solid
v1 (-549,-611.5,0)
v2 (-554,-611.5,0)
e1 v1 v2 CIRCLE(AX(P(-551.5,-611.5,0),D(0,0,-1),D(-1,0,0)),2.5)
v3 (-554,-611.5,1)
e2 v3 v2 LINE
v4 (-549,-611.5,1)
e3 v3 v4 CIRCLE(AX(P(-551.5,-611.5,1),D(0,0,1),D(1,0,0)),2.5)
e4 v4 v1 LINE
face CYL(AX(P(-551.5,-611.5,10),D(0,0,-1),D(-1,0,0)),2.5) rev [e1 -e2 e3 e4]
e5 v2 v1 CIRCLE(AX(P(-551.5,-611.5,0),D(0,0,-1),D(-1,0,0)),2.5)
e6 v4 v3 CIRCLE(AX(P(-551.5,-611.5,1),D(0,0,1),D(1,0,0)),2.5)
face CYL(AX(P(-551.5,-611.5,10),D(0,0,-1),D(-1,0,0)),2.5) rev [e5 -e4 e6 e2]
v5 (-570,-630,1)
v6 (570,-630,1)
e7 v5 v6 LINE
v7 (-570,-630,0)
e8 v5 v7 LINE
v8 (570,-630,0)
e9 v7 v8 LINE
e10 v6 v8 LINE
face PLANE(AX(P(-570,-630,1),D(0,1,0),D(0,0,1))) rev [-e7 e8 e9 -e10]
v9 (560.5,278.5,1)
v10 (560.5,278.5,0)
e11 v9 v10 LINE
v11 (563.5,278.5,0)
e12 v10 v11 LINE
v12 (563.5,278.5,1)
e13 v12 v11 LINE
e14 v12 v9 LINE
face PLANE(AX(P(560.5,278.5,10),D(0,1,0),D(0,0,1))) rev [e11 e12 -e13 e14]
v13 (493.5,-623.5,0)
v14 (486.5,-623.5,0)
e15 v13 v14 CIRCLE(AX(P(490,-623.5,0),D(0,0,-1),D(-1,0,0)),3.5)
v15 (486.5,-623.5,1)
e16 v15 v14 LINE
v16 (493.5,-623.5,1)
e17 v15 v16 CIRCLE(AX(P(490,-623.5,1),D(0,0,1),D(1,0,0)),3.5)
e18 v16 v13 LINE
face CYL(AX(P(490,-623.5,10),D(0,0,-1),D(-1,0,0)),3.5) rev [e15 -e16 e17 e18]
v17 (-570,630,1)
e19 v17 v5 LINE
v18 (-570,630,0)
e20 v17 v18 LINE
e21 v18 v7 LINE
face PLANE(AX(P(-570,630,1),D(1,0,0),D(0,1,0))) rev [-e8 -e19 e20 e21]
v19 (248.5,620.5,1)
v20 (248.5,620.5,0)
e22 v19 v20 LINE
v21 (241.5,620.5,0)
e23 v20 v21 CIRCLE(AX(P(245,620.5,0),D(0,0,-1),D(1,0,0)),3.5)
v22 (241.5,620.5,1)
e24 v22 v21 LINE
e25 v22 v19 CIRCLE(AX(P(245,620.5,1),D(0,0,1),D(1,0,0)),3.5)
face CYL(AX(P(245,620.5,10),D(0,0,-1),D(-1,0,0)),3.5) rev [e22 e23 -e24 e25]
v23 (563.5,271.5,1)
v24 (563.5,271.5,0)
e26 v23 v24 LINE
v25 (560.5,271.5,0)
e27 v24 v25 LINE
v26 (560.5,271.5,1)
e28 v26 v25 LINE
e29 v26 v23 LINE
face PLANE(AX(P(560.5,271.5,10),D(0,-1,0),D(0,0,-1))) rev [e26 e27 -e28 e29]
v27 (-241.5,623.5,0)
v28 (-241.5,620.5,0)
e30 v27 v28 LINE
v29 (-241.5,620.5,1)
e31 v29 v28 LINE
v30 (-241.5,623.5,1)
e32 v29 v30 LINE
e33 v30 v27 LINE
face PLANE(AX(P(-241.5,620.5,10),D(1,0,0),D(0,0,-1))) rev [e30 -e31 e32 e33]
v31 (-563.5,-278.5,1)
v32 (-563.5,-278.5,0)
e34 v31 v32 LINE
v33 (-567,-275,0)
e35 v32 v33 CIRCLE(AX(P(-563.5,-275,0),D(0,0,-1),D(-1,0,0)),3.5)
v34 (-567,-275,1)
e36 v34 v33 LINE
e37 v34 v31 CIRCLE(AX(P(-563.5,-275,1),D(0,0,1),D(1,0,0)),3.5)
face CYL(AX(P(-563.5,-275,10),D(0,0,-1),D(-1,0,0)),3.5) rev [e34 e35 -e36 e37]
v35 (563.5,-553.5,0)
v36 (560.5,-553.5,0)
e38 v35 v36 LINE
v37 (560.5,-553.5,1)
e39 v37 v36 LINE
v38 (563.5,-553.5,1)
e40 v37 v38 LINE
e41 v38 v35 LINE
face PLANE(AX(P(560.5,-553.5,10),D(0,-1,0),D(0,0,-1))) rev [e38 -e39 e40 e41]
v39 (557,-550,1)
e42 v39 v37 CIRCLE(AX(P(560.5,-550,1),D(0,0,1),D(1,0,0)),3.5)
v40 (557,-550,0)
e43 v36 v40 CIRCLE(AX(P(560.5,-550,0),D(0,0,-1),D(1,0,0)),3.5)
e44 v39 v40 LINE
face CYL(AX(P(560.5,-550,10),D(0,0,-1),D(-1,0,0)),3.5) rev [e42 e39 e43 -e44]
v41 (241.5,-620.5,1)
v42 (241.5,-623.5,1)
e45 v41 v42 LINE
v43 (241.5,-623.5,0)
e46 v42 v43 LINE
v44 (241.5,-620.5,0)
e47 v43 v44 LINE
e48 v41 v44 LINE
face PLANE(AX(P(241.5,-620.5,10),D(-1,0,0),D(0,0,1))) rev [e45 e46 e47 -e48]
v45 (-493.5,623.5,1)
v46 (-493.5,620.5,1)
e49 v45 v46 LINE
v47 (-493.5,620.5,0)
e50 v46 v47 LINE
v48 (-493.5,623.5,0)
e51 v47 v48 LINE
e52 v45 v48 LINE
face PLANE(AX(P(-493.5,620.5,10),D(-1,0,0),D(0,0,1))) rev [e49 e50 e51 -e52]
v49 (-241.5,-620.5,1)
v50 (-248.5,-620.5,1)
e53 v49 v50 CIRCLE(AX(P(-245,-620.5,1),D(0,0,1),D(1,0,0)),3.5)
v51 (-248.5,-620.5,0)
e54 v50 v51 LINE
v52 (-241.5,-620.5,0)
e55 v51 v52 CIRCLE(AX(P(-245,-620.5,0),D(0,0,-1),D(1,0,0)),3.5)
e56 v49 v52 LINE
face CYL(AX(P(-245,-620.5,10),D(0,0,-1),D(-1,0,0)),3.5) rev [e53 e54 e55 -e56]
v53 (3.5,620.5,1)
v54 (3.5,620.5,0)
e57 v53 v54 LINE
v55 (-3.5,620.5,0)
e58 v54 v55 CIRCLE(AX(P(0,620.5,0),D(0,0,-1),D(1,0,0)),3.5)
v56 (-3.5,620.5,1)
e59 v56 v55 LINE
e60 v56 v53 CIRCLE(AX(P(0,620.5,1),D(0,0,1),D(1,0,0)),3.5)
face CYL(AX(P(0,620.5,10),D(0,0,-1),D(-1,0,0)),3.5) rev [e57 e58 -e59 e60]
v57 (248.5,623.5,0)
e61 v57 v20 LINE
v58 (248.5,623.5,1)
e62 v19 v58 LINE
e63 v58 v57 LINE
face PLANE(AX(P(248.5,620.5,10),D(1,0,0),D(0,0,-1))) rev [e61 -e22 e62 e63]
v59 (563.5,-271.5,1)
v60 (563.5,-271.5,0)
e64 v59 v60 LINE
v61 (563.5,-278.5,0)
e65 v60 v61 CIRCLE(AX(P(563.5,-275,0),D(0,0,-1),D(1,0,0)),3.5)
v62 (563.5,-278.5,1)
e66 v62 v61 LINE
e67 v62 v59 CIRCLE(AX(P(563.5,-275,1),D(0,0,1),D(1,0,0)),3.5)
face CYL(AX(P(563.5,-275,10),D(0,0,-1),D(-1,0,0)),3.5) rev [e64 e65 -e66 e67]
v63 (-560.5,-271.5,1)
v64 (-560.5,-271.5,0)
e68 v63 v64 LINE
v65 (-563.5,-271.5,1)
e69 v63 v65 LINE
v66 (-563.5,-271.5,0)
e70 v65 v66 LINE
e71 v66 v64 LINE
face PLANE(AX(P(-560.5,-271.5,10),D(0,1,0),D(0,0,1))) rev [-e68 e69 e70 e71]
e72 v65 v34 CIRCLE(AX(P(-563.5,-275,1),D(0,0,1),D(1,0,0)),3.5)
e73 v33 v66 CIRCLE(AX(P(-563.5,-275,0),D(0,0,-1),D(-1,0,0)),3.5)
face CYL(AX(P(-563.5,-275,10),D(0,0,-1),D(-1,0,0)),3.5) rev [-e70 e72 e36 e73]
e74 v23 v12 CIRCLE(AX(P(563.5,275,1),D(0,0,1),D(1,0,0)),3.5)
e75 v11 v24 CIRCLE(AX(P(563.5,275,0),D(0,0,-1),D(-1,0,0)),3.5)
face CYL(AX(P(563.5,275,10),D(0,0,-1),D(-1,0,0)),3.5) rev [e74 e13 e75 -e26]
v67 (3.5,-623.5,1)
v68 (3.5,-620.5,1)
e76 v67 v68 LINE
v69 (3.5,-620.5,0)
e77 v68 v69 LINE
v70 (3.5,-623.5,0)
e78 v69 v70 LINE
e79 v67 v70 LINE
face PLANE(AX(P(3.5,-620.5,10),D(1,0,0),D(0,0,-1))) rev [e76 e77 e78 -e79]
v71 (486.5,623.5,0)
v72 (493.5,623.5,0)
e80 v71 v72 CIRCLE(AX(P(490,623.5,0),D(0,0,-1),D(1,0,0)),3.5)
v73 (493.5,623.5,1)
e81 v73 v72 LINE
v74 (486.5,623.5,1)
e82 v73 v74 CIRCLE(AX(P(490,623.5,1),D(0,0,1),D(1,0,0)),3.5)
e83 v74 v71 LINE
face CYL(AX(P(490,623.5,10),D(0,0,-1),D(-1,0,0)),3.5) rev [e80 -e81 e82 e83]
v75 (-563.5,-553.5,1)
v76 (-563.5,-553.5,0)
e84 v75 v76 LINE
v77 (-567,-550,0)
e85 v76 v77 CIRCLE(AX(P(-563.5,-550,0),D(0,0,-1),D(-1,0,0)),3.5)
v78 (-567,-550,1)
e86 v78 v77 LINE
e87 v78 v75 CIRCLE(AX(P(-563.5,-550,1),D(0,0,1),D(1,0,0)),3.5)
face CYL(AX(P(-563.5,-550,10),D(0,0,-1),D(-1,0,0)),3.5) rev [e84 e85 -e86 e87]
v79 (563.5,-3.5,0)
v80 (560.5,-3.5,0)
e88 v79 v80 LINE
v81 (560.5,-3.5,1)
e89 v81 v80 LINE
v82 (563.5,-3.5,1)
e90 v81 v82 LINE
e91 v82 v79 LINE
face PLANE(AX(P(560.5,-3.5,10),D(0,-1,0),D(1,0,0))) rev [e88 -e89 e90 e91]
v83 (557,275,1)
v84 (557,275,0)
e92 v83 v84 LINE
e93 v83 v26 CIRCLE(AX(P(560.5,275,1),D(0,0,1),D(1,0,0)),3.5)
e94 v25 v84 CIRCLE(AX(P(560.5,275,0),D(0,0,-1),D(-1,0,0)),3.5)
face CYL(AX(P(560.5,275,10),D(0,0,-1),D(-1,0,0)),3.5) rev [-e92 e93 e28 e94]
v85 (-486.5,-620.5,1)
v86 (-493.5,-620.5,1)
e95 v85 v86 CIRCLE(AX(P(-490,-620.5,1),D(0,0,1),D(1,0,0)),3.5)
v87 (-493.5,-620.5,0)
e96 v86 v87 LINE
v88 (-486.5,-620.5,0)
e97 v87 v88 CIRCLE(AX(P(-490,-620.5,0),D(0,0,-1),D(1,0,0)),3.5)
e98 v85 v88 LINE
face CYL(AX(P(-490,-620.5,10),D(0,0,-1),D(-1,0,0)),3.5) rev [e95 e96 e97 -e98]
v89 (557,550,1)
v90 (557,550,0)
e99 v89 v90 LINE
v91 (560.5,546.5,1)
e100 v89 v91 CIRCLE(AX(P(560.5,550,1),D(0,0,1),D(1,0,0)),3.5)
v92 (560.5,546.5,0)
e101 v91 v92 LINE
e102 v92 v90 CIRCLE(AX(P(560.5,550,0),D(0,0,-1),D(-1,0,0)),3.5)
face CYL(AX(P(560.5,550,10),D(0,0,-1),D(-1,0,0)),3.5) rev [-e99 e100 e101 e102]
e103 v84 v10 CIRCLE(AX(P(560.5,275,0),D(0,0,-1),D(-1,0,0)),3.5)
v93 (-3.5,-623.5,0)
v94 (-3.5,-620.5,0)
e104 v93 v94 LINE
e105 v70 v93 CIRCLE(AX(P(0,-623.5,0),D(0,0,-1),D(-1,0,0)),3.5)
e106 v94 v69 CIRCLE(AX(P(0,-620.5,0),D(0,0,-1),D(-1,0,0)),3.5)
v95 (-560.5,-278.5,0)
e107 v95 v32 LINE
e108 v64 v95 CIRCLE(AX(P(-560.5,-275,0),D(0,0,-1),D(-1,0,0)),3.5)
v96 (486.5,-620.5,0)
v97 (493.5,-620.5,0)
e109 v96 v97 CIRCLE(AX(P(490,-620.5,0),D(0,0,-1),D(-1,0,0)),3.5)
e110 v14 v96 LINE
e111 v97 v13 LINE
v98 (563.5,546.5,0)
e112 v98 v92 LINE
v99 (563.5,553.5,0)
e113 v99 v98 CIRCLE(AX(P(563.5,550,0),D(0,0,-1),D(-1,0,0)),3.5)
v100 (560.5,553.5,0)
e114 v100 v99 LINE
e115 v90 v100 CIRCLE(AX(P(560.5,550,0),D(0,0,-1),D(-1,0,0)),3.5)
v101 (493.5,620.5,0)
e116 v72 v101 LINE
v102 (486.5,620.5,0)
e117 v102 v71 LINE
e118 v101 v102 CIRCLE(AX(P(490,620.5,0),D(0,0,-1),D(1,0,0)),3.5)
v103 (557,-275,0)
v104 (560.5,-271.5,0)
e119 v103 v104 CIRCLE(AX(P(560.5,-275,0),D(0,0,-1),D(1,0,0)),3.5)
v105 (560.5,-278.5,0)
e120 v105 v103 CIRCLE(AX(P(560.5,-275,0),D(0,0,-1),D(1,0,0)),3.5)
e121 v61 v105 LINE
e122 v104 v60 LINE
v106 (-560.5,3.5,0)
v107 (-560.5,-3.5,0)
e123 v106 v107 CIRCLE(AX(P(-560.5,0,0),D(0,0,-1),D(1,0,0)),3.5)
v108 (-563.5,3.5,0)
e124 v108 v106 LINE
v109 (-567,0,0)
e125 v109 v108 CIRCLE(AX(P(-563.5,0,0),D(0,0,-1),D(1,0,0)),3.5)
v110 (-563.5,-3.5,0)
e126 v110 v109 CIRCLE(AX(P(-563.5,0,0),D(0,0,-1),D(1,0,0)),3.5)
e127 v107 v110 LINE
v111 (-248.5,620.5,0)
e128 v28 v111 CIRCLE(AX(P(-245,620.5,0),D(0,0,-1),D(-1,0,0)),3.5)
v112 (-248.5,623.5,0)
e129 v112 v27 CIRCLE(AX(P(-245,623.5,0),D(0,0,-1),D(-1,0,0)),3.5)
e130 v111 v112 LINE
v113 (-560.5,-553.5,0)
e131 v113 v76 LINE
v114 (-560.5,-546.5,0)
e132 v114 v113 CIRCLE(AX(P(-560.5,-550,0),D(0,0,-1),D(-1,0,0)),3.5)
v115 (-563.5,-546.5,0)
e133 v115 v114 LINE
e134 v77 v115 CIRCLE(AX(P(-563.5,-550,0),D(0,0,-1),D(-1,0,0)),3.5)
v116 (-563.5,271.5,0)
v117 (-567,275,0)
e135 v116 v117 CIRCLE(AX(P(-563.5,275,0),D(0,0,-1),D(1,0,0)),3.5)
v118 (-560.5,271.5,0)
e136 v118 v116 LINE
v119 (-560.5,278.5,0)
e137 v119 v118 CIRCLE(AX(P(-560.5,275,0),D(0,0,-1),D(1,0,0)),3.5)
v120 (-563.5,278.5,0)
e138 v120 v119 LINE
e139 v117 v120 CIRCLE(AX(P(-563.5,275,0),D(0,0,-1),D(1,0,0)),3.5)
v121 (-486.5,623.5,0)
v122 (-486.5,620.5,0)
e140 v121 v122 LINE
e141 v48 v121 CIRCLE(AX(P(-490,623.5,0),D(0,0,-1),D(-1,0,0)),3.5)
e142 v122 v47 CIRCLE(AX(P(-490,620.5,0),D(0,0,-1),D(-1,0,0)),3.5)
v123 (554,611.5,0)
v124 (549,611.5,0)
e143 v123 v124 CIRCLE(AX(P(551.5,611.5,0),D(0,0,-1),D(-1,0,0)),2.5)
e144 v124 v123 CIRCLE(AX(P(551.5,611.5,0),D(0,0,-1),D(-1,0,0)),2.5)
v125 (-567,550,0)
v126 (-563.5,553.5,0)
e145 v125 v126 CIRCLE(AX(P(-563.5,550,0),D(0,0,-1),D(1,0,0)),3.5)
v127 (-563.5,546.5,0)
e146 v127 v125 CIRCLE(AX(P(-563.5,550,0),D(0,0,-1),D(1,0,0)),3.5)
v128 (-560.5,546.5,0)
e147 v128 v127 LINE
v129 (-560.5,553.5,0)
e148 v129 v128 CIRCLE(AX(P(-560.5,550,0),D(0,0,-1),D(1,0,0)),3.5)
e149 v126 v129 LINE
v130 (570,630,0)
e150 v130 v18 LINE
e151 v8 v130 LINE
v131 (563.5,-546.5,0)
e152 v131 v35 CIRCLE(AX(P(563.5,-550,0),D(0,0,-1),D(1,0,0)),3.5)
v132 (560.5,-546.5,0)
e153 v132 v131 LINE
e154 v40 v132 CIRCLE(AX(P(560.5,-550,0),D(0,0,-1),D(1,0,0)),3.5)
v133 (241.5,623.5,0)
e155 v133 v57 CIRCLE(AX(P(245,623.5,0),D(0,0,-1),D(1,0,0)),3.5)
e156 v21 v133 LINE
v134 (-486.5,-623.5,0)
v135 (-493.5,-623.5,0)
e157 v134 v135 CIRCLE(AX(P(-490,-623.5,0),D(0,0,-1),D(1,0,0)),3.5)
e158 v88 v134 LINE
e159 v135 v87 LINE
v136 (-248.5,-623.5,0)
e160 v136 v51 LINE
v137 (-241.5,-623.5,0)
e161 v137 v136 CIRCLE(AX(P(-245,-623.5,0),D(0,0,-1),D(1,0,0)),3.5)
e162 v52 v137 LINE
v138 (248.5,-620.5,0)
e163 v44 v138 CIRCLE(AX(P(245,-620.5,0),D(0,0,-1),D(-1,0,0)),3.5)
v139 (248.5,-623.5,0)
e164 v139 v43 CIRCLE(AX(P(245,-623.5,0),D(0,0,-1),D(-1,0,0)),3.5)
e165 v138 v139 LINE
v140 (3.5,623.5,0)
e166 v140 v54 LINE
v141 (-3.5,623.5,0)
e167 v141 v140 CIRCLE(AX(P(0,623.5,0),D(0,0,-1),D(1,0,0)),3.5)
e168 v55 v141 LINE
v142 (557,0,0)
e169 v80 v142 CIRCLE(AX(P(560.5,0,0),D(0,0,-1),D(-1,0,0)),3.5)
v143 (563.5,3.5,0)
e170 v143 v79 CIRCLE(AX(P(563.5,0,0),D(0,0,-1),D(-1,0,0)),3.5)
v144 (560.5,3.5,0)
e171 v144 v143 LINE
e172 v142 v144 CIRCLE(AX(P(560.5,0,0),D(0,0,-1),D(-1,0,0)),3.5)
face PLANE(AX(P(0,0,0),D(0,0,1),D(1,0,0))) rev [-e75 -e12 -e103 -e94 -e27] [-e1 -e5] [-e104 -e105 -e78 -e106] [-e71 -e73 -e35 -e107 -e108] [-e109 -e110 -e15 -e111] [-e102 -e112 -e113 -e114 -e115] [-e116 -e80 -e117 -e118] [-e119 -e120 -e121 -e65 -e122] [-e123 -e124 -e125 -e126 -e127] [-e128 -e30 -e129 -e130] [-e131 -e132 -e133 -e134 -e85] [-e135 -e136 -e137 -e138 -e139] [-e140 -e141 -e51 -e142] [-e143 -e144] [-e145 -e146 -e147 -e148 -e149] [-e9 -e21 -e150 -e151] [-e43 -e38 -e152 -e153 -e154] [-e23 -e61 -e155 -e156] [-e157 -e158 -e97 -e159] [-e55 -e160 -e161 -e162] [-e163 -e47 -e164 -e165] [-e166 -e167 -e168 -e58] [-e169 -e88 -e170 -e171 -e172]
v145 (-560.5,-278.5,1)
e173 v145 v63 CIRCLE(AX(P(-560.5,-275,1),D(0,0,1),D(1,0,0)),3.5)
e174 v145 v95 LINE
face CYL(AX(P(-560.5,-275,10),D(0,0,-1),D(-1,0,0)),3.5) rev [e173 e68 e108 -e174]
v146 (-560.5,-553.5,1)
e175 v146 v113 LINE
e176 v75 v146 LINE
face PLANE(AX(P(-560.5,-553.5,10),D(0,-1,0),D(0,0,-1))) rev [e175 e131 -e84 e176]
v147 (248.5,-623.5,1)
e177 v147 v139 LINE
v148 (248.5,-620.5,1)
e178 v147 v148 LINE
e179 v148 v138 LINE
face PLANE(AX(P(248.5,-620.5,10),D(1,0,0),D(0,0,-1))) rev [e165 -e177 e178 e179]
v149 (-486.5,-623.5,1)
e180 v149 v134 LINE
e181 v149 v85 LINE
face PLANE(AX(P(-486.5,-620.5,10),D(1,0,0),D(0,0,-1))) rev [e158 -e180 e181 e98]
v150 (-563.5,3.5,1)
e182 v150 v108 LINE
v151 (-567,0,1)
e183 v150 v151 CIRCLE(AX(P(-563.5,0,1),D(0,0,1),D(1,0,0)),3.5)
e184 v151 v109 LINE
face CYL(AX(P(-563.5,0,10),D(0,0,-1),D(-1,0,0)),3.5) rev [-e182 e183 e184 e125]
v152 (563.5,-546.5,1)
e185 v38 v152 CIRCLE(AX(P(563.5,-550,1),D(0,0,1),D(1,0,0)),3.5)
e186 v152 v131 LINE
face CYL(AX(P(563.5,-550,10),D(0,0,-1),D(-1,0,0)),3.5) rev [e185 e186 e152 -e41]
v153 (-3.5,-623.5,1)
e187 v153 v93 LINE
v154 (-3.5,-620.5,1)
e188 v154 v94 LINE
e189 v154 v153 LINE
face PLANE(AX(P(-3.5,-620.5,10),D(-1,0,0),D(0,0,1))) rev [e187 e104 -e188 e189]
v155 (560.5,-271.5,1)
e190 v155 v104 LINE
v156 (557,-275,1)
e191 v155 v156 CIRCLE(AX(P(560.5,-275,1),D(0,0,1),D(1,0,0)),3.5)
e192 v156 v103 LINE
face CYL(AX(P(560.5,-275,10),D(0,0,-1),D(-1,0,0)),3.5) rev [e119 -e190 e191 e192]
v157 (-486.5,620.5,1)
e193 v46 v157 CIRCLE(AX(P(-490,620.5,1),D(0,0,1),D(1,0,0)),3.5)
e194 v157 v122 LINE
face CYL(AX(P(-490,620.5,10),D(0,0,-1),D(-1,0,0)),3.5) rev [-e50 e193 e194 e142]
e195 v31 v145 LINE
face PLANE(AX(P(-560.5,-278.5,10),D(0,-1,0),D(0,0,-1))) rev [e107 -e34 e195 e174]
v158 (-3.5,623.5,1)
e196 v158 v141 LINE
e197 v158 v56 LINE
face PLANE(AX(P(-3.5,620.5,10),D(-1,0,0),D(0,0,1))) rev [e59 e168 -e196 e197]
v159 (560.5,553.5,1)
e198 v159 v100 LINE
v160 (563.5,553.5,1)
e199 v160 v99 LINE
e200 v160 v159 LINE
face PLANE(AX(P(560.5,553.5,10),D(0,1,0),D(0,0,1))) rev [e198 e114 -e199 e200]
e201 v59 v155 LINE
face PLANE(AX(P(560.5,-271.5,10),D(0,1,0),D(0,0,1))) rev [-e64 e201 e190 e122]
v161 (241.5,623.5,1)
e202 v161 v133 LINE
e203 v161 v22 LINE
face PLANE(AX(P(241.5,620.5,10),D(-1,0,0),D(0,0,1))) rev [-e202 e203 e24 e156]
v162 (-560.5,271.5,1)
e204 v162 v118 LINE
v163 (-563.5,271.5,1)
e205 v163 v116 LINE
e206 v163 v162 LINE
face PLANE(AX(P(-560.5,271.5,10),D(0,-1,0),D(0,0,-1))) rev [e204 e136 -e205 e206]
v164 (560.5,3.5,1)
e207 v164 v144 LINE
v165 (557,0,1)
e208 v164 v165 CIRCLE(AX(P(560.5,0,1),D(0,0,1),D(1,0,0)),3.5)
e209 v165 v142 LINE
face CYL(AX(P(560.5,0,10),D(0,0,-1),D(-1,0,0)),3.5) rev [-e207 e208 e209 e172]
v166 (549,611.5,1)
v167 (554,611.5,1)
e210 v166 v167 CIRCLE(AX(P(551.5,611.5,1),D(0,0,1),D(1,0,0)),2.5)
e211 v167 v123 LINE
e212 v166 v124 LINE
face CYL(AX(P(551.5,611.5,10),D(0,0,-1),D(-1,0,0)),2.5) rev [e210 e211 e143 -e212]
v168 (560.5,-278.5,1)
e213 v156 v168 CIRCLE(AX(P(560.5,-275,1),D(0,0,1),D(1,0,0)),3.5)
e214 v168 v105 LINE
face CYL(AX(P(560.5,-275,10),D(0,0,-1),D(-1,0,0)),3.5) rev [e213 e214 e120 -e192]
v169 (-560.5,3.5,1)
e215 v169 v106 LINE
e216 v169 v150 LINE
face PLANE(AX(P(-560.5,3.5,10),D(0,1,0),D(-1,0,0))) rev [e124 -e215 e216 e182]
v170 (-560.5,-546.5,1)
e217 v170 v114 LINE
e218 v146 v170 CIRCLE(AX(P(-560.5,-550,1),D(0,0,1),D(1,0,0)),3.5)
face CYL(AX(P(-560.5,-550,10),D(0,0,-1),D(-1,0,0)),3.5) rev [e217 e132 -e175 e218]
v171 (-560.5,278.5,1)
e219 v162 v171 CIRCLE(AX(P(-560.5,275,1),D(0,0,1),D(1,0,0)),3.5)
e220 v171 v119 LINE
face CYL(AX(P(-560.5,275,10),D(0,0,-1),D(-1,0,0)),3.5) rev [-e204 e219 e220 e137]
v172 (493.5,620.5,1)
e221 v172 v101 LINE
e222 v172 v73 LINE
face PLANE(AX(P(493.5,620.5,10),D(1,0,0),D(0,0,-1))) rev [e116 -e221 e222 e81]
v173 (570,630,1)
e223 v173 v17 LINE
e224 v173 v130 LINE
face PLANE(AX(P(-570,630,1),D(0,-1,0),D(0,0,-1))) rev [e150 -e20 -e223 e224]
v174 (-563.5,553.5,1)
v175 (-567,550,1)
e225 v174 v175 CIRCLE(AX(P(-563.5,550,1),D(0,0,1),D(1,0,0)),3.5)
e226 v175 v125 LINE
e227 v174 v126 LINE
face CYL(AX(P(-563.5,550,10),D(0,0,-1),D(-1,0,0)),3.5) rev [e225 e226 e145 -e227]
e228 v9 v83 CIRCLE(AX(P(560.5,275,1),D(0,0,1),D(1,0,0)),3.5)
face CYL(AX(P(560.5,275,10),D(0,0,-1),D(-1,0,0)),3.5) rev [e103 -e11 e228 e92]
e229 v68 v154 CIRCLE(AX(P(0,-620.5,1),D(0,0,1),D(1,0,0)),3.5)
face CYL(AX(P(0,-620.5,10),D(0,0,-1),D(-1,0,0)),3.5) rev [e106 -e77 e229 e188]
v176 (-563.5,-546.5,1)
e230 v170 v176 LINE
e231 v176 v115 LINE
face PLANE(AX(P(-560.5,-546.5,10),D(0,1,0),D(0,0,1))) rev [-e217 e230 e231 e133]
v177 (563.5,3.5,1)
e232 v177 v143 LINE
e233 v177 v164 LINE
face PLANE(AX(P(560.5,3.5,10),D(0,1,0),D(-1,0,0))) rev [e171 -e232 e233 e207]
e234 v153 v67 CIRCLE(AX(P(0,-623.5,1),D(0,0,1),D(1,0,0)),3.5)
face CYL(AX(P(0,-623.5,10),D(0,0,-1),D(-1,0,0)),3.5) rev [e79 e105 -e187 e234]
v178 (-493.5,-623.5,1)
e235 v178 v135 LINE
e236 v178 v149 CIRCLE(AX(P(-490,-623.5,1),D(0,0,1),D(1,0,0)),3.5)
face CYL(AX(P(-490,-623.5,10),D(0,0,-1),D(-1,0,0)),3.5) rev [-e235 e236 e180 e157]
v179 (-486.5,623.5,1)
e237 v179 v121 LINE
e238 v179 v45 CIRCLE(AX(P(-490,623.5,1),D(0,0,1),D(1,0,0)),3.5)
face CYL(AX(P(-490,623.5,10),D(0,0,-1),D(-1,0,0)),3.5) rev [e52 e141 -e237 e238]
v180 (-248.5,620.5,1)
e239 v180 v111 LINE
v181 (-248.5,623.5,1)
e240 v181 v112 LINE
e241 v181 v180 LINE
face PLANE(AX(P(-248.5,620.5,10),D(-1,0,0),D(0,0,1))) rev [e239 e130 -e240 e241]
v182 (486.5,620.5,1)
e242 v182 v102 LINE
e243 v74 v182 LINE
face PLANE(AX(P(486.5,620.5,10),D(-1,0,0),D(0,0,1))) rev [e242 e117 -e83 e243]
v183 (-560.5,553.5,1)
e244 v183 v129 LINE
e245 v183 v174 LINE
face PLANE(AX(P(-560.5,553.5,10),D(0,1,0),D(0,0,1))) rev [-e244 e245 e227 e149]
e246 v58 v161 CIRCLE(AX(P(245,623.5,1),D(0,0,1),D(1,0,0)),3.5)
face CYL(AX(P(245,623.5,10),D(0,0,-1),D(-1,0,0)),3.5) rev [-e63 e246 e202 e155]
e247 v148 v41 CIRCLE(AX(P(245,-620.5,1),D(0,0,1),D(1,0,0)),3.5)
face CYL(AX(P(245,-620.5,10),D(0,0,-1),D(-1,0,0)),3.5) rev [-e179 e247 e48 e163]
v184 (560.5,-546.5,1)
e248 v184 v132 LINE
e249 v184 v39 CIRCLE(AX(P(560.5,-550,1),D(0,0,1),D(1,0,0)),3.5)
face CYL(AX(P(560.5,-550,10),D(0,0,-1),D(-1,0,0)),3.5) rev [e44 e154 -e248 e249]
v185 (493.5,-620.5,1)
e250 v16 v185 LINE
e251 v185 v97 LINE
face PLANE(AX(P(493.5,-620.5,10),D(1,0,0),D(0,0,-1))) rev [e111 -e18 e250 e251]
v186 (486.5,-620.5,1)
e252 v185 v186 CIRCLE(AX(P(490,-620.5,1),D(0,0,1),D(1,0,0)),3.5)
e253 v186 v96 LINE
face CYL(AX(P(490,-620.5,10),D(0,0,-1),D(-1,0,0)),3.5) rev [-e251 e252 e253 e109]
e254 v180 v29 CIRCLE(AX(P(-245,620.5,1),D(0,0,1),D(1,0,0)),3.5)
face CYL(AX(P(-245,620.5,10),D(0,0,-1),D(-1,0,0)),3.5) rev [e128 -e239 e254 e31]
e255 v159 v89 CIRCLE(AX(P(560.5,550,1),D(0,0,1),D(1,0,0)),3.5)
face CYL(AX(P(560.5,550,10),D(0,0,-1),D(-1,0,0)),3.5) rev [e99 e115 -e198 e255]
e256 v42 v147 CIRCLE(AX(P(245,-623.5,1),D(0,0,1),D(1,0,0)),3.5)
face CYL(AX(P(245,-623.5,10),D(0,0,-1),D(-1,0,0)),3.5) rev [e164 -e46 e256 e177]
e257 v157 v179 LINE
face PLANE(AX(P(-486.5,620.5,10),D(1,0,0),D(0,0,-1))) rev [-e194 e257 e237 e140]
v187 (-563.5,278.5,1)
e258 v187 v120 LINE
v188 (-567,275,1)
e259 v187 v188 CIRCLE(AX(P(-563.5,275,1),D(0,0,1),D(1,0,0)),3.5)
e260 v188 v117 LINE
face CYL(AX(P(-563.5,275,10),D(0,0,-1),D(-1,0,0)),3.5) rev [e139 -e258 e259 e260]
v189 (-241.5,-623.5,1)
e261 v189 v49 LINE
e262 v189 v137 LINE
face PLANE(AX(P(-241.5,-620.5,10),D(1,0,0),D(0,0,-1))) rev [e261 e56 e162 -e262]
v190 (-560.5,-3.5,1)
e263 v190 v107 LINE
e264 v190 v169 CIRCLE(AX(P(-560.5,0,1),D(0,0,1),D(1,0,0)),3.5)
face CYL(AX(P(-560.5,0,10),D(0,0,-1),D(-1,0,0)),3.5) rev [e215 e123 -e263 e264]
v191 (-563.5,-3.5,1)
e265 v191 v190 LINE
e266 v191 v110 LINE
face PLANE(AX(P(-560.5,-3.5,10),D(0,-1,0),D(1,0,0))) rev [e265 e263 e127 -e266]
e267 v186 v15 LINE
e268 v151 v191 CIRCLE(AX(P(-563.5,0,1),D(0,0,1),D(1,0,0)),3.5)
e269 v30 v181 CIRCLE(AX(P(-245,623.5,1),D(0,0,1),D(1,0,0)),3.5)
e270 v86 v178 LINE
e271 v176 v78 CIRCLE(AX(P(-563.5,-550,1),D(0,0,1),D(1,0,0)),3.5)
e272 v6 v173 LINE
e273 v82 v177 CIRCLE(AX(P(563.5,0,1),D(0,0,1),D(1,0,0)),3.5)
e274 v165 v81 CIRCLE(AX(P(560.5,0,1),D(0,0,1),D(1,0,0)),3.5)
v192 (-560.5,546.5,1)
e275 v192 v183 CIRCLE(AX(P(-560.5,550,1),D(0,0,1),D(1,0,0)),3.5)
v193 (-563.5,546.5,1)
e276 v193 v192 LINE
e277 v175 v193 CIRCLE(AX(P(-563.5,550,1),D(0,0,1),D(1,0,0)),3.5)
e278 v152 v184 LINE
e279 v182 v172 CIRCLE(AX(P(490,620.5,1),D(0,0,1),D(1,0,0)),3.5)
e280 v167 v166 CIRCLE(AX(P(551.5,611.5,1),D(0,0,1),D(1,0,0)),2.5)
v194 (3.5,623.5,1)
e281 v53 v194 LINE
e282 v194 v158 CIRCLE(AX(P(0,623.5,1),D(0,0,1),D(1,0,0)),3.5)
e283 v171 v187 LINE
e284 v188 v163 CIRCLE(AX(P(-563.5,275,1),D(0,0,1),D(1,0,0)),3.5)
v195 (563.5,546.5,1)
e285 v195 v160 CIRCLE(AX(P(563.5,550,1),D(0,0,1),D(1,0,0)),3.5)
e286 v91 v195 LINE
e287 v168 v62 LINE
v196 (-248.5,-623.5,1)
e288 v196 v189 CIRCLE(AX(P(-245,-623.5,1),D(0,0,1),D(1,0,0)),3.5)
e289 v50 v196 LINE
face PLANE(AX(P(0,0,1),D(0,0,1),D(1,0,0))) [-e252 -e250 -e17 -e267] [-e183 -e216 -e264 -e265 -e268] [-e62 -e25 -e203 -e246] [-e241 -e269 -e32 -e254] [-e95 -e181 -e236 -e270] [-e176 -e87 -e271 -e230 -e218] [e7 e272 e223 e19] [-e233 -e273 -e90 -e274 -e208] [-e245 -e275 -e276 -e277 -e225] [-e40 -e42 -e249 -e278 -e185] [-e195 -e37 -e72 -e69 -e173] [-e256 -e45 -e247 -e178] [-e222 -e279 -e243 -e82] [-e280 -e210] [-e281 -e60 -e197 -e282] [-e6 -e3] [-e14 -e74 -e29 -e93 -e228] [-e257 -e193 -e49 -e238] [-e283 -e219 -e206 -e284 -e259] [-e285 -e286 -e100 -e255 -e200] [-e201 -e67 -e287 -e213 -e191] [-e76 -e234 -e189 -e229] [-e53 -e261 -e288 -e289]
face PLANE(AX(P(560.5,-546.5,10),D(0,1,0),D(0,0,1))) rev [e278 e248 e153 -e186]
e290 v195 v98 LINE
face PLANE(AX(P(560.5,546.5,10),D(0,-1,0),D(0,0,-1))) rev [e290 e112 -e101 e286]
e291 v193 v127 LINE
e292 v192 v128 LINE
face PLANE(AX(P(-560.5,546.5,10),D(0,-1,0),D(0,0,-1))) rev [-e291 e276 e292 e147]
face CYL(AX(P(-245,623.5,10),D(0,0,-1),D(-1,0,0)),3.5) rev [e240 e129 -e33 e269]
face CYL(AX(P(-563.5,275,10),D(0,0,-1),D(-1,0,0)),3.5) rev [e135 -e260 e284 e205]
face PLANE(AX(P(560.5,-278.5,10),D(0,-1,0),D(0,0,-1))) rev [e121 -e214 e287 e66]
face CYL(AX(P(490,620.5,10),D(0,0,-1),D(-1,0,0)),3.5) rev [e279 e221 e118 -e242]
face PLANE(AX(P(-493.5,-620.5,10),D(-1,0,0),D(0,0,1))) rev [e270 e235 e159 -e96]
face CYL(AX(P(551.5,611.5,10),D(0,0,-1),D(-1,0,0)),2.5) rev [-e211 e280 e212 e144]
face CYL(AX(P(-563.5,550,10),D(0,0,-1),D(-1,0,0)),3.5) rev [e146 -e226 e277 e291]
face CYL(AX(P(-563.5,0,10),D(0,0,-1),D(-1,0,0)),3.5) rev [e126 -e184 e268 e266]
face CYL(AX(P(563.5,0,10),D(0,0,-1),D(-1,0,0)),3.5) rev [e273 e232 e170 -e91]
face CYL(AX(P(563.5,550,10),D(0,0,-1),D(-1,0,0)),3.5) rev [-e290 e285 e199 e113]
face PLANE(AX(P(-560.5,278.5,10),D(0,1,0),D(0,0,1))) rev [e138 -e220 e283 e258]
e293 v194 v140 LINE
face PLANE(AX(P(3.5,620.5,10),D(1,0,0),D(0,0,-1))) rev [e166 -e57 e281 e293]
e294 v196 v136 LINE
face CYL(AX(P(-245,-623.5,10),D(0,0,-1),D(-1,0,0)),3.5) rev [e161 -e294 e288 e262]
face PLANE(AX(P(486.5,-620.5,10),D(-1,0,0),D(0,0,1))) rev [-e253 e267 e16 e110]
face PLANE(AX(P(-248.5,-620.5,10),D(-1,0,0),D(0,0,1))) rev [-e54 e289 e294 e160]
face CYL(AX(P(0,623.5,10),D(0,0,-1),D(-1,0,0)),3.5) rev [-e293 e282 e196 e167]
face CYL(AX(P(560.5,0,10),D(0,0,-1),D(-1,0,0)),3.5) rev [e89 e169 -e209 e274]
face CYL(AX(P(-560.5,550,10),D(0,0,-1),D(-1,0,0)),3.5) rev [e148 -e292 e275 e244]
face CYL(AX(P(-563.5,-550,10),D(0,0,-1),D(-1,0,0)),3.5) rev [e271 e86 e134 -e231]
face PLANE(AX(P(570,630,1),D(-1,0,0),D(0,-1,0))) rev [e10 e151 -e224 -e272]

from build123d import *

# Parameters (mm, degrees)
SKETCH_1_W          = 1140
SKETCH_1_H          = 1260
EXTRUDE_1_DEPTH     = 1
SKETCH_3_R          = 2.5
CUT_EXTRUDE_2_DEPTH = 10
CUT_EXTRUDE_3_DEPTH = 10


with BuildPart() as part:
    # 草图1 → 凸台-拉伸1 (new body)
    with BuildSketch(Plane.XY):
        Rectangle(SKETCH_1_W, SKETCH_1_H)
    extrude(amount=EXTRUDE_1_DEPTH)

    # 草图3 → 切除-拉伸2 (cut)
    with BuildSketch(Plane(origin=(0, 0, 0), x_dir=(-1, 0, 0), z_dir=(0, 0, -1))):
        with Locations((551.5, -611.5)):
            Circle(SKETCH_3_R)
        with Locations((-551.5, 611.5)):
            Circle(SKETCH_3_R)
    extrude(amount=-CUT_EXTRUDE_2_DEPTH, mode=Mode.SUBTRACT)

    # 草图4 → 切除-拉伸3 (cut)
    with BuildSketch(Plane(origin=(0, 0, 0), x_dir=(-1, 0, 0), z_dir=(0, 0, -1))):
        with BuildLine():
            Line((3.5, -620.5), (3.5, -623.5))
            ThreePointArc((3.5, -623.5), (0, -627), (-3.5, -623.5))
            Line((-3.5, -623.5), (-3.5, -620.5))
            ThreePointArc((-3.5, -620.5), (0, -617), (3.5, -620.5))
        make_face()
        with BuildLine():
            Line((-241.5, -620.5), (-241.5, -623.5))
            ThreePointArc((-241.5, -623.5), (-245, -627), (-248.5, -623.5))
            Line((-248.5, -623.5), (-248.5, -620.5))
            ThreePointArc((-248.5, -620.5), (-245, -617), (-241.5, -620.5))
        make_face()
        with BuildLine():
            Line((-486.5, -620.5), (-486.5, -623.5))
            ThreePointArc((-486.5, -623.5), (-490, -627), (-493.5, -623.5))
            Line((-493.5, -623.5), (-493.5, -620.5))
            ThreePointArc((-493.5, -620.5), (-490, -617), (-486.5, -620.5))
        make_face()
        with BuildLine():
            Line((486.5, -620.5), (486.5, -623.5))
            ThreePointArc((486.5, -623.5), (490, -627), (493.5, -623.5))
            Line((493.5, -623.5), (493.5, -620.5))
            ThreePointArc((493.5, -620.5), (490, -617), (486.5, -620.5))
        make_face()
        with BuildLine():
            Line((241.5, -620.5), (241.5, -623.5))
            ThreePointArc((241.5, -623.5), (245, -627), (248.5, -623.5))
            Line((248.5, -623.5), (248.5, -620.5))
            ThreePointArc((248.5, -620.5), (245, -617), (241.5, -620.5))
        make_face()
        with BuildLine():
            Line((-560.5, -3.5), (-563.5, -3.5))
            ThreePointArc((-563.5, -3.5), (-567, 0), (-563.5, 3.5))
            Line((-563.5, 3.5), (-560.5, 3.5))
            ThreePointArc((-560.5, 3.5), (-557, 0), (-560.5, -3.5))
        make_face()
        with BuildLine():
            Line((-560.5, 271.5), (-563.5, 271.5))
            ThreePointArc((-563.5, 271.5), (-567, 275), (-563.5, 278.5))
            Line((-563.5, 278.5), (-560.5, 278.5))
            ThreePointArc((-560.5, 278.5), (-557, 275), (-560.5, 271.5))
        make_face()
        with BuildLine():
            Line((-560.5, 546.5), (-563.5, 546.5))
            ThreePointArc((-563.5, 546.5), (-567, 550), (-563.5, 553.5))
            Line((-563.5, 553.5), (-560.5, 553.5))
            ThreePointArc((-560.5, 553.5), (-557, 550), (-560.5, 546.5))
        make_face()
        with BuildLine():
            Line((-560.5, -546.5), (-563.5, -546.5))
            ThreePointArc((-563.5, -546.5), (-567, -550), (-563.5, -553.5))
            Line((-563.5, -553.5), (-560.5, -553.5))
            ThreePointArc((-560.5, -553.5), (-557, -550), (-560.5, -546.5))
        make_face()
        with BuildLine():
            Line((-560.5, -271.5), (-563.5, -271.5))
            ThreePointArc((-563.5, -271.5), (-567, -275), (-563.5, -278.5))
            Line((-563.5, -278.5), (-560.5, -278.5))
            ThreePointArc((-560.5, -278.5), (-557, -275), (-560.5, -271.5))
        make_face()
        with BuildLine():
            Line((241.5, 620.5), (241.5, 623.5))
            ThreePointArc((241.5, 623.5), (245, 627), (248.5, 623.5))
            Line((248.5, 623.5), (248.5, 620.5))
            ThreePointArc((248.5, 620.5), (245, 617), (241.5, 620.5))
        make_face()
        with BuildLine():
            Line((486.5, 620.5), (486.5, 623.5))
            ThreePointArc((486.5, 623.5), (490, 627), (493.5, 623.5))
            Line((493.5, 623.5), (493.5, 620.5))
            ThreePointArc((493.5, 620.5), (490, 617), (486.5, 620.5))
        make_face()
        with BuildLine():
            Line((-486.5, 620.5), (-486.5, 623.5))
            ThreePointArc((-486.5, 623.5), (-490, 627), (-493.5, 623.5))
            Line((-493.5, 623.5), (-493.5, 620.5))
            ThreePointArc((-493.5, 620.5), (-490, 617), (-486.5, 620.5))
        make_face()
        with BuildLine():
            Line((-241.5, 620.5), (-241.5, 623.5))
            ThreePointArc((-241.5, 623.5), (-245, 627), (-248.5, 623.5))
            Line((-248.5, 623.5), (-248.5, 620.5))
            ThreePointArc((-248.5, 620.5), (-245, 617), (-241.5, 620.5))
        make_face()
        with BuildLine():
            Line((3.5, 620.5), (3.5, 623.5))
            ThreePointArc((3.5, 623.5), (0, 627), (-3.5, 623.5))
            Line((-3.5, 623.5), (-3.5, 620.5))
            ThreePointArc((-3.5, 620.5), (0, 617), (3.5, 620.5))
        make_face()
        with BuildLine():
            Line((560.5, 546.5), (563.5, 546.5))
            ThreePointArc((563.5, 546.5), (567, 550), (563.5, 553.5))
            Line((563.5, 553.5), (560.5, 553.5))
            ThreePointArc((560.5, 553.5), (557, 550), (560.5, 546.5))
        make_face()
        with BuildLine():
            Line((560.5, -271.5), (563.5, -271.5))
            ThreePointArc((563.5, -271.5), (567, -275), (563.5, -278.5))
            Line((563.5, -278.5), (560.5, -278.5))
            ThreePointArc((560.5, -278.5), (557, -275), (560.5, -271.5))
        make_face()
        with BuildLine():
            Line((560.5, -546.5), (563.5, -546.5))
            ThreePointArc((563.5, -546.5), (567, -550), (563.5, -553.5))
            Line((563.5, -553.5), (560.5, -553.5))
            ThreePointArc((560.5, -553.5), (557, -550), (560.5, -546.5))
        make_face()
        with BuildLine():
            Line((560.5, 271.5), (563.5, 271.5))
            ThreePointArc((563.5, 271.5), (567, 275), (563.5, 278.5))
            Line((563.5, 278.5), (560.5, 278.5))
            ThreePointArc((560.5, 278.5), (557, 275), (560.5, 271.5))
        make_face()
        with BuildLine():
            Line((560.5, -3.5), (563.5, -3.5))
            ThreePointArc((563.5, -3.5), (567, 0), (563.5, 3.5))
            Line((563.5, 3.5), (560.5, 3.5))
            ThreePointArc((560.5, 3.5), (557, 0), (560.5, -3.5))
        make_face()
    extrude(amount=-CUT_EXTRUDE_3_DEPTH, mode=Mode.SUBTRACT)


solid = part.part
